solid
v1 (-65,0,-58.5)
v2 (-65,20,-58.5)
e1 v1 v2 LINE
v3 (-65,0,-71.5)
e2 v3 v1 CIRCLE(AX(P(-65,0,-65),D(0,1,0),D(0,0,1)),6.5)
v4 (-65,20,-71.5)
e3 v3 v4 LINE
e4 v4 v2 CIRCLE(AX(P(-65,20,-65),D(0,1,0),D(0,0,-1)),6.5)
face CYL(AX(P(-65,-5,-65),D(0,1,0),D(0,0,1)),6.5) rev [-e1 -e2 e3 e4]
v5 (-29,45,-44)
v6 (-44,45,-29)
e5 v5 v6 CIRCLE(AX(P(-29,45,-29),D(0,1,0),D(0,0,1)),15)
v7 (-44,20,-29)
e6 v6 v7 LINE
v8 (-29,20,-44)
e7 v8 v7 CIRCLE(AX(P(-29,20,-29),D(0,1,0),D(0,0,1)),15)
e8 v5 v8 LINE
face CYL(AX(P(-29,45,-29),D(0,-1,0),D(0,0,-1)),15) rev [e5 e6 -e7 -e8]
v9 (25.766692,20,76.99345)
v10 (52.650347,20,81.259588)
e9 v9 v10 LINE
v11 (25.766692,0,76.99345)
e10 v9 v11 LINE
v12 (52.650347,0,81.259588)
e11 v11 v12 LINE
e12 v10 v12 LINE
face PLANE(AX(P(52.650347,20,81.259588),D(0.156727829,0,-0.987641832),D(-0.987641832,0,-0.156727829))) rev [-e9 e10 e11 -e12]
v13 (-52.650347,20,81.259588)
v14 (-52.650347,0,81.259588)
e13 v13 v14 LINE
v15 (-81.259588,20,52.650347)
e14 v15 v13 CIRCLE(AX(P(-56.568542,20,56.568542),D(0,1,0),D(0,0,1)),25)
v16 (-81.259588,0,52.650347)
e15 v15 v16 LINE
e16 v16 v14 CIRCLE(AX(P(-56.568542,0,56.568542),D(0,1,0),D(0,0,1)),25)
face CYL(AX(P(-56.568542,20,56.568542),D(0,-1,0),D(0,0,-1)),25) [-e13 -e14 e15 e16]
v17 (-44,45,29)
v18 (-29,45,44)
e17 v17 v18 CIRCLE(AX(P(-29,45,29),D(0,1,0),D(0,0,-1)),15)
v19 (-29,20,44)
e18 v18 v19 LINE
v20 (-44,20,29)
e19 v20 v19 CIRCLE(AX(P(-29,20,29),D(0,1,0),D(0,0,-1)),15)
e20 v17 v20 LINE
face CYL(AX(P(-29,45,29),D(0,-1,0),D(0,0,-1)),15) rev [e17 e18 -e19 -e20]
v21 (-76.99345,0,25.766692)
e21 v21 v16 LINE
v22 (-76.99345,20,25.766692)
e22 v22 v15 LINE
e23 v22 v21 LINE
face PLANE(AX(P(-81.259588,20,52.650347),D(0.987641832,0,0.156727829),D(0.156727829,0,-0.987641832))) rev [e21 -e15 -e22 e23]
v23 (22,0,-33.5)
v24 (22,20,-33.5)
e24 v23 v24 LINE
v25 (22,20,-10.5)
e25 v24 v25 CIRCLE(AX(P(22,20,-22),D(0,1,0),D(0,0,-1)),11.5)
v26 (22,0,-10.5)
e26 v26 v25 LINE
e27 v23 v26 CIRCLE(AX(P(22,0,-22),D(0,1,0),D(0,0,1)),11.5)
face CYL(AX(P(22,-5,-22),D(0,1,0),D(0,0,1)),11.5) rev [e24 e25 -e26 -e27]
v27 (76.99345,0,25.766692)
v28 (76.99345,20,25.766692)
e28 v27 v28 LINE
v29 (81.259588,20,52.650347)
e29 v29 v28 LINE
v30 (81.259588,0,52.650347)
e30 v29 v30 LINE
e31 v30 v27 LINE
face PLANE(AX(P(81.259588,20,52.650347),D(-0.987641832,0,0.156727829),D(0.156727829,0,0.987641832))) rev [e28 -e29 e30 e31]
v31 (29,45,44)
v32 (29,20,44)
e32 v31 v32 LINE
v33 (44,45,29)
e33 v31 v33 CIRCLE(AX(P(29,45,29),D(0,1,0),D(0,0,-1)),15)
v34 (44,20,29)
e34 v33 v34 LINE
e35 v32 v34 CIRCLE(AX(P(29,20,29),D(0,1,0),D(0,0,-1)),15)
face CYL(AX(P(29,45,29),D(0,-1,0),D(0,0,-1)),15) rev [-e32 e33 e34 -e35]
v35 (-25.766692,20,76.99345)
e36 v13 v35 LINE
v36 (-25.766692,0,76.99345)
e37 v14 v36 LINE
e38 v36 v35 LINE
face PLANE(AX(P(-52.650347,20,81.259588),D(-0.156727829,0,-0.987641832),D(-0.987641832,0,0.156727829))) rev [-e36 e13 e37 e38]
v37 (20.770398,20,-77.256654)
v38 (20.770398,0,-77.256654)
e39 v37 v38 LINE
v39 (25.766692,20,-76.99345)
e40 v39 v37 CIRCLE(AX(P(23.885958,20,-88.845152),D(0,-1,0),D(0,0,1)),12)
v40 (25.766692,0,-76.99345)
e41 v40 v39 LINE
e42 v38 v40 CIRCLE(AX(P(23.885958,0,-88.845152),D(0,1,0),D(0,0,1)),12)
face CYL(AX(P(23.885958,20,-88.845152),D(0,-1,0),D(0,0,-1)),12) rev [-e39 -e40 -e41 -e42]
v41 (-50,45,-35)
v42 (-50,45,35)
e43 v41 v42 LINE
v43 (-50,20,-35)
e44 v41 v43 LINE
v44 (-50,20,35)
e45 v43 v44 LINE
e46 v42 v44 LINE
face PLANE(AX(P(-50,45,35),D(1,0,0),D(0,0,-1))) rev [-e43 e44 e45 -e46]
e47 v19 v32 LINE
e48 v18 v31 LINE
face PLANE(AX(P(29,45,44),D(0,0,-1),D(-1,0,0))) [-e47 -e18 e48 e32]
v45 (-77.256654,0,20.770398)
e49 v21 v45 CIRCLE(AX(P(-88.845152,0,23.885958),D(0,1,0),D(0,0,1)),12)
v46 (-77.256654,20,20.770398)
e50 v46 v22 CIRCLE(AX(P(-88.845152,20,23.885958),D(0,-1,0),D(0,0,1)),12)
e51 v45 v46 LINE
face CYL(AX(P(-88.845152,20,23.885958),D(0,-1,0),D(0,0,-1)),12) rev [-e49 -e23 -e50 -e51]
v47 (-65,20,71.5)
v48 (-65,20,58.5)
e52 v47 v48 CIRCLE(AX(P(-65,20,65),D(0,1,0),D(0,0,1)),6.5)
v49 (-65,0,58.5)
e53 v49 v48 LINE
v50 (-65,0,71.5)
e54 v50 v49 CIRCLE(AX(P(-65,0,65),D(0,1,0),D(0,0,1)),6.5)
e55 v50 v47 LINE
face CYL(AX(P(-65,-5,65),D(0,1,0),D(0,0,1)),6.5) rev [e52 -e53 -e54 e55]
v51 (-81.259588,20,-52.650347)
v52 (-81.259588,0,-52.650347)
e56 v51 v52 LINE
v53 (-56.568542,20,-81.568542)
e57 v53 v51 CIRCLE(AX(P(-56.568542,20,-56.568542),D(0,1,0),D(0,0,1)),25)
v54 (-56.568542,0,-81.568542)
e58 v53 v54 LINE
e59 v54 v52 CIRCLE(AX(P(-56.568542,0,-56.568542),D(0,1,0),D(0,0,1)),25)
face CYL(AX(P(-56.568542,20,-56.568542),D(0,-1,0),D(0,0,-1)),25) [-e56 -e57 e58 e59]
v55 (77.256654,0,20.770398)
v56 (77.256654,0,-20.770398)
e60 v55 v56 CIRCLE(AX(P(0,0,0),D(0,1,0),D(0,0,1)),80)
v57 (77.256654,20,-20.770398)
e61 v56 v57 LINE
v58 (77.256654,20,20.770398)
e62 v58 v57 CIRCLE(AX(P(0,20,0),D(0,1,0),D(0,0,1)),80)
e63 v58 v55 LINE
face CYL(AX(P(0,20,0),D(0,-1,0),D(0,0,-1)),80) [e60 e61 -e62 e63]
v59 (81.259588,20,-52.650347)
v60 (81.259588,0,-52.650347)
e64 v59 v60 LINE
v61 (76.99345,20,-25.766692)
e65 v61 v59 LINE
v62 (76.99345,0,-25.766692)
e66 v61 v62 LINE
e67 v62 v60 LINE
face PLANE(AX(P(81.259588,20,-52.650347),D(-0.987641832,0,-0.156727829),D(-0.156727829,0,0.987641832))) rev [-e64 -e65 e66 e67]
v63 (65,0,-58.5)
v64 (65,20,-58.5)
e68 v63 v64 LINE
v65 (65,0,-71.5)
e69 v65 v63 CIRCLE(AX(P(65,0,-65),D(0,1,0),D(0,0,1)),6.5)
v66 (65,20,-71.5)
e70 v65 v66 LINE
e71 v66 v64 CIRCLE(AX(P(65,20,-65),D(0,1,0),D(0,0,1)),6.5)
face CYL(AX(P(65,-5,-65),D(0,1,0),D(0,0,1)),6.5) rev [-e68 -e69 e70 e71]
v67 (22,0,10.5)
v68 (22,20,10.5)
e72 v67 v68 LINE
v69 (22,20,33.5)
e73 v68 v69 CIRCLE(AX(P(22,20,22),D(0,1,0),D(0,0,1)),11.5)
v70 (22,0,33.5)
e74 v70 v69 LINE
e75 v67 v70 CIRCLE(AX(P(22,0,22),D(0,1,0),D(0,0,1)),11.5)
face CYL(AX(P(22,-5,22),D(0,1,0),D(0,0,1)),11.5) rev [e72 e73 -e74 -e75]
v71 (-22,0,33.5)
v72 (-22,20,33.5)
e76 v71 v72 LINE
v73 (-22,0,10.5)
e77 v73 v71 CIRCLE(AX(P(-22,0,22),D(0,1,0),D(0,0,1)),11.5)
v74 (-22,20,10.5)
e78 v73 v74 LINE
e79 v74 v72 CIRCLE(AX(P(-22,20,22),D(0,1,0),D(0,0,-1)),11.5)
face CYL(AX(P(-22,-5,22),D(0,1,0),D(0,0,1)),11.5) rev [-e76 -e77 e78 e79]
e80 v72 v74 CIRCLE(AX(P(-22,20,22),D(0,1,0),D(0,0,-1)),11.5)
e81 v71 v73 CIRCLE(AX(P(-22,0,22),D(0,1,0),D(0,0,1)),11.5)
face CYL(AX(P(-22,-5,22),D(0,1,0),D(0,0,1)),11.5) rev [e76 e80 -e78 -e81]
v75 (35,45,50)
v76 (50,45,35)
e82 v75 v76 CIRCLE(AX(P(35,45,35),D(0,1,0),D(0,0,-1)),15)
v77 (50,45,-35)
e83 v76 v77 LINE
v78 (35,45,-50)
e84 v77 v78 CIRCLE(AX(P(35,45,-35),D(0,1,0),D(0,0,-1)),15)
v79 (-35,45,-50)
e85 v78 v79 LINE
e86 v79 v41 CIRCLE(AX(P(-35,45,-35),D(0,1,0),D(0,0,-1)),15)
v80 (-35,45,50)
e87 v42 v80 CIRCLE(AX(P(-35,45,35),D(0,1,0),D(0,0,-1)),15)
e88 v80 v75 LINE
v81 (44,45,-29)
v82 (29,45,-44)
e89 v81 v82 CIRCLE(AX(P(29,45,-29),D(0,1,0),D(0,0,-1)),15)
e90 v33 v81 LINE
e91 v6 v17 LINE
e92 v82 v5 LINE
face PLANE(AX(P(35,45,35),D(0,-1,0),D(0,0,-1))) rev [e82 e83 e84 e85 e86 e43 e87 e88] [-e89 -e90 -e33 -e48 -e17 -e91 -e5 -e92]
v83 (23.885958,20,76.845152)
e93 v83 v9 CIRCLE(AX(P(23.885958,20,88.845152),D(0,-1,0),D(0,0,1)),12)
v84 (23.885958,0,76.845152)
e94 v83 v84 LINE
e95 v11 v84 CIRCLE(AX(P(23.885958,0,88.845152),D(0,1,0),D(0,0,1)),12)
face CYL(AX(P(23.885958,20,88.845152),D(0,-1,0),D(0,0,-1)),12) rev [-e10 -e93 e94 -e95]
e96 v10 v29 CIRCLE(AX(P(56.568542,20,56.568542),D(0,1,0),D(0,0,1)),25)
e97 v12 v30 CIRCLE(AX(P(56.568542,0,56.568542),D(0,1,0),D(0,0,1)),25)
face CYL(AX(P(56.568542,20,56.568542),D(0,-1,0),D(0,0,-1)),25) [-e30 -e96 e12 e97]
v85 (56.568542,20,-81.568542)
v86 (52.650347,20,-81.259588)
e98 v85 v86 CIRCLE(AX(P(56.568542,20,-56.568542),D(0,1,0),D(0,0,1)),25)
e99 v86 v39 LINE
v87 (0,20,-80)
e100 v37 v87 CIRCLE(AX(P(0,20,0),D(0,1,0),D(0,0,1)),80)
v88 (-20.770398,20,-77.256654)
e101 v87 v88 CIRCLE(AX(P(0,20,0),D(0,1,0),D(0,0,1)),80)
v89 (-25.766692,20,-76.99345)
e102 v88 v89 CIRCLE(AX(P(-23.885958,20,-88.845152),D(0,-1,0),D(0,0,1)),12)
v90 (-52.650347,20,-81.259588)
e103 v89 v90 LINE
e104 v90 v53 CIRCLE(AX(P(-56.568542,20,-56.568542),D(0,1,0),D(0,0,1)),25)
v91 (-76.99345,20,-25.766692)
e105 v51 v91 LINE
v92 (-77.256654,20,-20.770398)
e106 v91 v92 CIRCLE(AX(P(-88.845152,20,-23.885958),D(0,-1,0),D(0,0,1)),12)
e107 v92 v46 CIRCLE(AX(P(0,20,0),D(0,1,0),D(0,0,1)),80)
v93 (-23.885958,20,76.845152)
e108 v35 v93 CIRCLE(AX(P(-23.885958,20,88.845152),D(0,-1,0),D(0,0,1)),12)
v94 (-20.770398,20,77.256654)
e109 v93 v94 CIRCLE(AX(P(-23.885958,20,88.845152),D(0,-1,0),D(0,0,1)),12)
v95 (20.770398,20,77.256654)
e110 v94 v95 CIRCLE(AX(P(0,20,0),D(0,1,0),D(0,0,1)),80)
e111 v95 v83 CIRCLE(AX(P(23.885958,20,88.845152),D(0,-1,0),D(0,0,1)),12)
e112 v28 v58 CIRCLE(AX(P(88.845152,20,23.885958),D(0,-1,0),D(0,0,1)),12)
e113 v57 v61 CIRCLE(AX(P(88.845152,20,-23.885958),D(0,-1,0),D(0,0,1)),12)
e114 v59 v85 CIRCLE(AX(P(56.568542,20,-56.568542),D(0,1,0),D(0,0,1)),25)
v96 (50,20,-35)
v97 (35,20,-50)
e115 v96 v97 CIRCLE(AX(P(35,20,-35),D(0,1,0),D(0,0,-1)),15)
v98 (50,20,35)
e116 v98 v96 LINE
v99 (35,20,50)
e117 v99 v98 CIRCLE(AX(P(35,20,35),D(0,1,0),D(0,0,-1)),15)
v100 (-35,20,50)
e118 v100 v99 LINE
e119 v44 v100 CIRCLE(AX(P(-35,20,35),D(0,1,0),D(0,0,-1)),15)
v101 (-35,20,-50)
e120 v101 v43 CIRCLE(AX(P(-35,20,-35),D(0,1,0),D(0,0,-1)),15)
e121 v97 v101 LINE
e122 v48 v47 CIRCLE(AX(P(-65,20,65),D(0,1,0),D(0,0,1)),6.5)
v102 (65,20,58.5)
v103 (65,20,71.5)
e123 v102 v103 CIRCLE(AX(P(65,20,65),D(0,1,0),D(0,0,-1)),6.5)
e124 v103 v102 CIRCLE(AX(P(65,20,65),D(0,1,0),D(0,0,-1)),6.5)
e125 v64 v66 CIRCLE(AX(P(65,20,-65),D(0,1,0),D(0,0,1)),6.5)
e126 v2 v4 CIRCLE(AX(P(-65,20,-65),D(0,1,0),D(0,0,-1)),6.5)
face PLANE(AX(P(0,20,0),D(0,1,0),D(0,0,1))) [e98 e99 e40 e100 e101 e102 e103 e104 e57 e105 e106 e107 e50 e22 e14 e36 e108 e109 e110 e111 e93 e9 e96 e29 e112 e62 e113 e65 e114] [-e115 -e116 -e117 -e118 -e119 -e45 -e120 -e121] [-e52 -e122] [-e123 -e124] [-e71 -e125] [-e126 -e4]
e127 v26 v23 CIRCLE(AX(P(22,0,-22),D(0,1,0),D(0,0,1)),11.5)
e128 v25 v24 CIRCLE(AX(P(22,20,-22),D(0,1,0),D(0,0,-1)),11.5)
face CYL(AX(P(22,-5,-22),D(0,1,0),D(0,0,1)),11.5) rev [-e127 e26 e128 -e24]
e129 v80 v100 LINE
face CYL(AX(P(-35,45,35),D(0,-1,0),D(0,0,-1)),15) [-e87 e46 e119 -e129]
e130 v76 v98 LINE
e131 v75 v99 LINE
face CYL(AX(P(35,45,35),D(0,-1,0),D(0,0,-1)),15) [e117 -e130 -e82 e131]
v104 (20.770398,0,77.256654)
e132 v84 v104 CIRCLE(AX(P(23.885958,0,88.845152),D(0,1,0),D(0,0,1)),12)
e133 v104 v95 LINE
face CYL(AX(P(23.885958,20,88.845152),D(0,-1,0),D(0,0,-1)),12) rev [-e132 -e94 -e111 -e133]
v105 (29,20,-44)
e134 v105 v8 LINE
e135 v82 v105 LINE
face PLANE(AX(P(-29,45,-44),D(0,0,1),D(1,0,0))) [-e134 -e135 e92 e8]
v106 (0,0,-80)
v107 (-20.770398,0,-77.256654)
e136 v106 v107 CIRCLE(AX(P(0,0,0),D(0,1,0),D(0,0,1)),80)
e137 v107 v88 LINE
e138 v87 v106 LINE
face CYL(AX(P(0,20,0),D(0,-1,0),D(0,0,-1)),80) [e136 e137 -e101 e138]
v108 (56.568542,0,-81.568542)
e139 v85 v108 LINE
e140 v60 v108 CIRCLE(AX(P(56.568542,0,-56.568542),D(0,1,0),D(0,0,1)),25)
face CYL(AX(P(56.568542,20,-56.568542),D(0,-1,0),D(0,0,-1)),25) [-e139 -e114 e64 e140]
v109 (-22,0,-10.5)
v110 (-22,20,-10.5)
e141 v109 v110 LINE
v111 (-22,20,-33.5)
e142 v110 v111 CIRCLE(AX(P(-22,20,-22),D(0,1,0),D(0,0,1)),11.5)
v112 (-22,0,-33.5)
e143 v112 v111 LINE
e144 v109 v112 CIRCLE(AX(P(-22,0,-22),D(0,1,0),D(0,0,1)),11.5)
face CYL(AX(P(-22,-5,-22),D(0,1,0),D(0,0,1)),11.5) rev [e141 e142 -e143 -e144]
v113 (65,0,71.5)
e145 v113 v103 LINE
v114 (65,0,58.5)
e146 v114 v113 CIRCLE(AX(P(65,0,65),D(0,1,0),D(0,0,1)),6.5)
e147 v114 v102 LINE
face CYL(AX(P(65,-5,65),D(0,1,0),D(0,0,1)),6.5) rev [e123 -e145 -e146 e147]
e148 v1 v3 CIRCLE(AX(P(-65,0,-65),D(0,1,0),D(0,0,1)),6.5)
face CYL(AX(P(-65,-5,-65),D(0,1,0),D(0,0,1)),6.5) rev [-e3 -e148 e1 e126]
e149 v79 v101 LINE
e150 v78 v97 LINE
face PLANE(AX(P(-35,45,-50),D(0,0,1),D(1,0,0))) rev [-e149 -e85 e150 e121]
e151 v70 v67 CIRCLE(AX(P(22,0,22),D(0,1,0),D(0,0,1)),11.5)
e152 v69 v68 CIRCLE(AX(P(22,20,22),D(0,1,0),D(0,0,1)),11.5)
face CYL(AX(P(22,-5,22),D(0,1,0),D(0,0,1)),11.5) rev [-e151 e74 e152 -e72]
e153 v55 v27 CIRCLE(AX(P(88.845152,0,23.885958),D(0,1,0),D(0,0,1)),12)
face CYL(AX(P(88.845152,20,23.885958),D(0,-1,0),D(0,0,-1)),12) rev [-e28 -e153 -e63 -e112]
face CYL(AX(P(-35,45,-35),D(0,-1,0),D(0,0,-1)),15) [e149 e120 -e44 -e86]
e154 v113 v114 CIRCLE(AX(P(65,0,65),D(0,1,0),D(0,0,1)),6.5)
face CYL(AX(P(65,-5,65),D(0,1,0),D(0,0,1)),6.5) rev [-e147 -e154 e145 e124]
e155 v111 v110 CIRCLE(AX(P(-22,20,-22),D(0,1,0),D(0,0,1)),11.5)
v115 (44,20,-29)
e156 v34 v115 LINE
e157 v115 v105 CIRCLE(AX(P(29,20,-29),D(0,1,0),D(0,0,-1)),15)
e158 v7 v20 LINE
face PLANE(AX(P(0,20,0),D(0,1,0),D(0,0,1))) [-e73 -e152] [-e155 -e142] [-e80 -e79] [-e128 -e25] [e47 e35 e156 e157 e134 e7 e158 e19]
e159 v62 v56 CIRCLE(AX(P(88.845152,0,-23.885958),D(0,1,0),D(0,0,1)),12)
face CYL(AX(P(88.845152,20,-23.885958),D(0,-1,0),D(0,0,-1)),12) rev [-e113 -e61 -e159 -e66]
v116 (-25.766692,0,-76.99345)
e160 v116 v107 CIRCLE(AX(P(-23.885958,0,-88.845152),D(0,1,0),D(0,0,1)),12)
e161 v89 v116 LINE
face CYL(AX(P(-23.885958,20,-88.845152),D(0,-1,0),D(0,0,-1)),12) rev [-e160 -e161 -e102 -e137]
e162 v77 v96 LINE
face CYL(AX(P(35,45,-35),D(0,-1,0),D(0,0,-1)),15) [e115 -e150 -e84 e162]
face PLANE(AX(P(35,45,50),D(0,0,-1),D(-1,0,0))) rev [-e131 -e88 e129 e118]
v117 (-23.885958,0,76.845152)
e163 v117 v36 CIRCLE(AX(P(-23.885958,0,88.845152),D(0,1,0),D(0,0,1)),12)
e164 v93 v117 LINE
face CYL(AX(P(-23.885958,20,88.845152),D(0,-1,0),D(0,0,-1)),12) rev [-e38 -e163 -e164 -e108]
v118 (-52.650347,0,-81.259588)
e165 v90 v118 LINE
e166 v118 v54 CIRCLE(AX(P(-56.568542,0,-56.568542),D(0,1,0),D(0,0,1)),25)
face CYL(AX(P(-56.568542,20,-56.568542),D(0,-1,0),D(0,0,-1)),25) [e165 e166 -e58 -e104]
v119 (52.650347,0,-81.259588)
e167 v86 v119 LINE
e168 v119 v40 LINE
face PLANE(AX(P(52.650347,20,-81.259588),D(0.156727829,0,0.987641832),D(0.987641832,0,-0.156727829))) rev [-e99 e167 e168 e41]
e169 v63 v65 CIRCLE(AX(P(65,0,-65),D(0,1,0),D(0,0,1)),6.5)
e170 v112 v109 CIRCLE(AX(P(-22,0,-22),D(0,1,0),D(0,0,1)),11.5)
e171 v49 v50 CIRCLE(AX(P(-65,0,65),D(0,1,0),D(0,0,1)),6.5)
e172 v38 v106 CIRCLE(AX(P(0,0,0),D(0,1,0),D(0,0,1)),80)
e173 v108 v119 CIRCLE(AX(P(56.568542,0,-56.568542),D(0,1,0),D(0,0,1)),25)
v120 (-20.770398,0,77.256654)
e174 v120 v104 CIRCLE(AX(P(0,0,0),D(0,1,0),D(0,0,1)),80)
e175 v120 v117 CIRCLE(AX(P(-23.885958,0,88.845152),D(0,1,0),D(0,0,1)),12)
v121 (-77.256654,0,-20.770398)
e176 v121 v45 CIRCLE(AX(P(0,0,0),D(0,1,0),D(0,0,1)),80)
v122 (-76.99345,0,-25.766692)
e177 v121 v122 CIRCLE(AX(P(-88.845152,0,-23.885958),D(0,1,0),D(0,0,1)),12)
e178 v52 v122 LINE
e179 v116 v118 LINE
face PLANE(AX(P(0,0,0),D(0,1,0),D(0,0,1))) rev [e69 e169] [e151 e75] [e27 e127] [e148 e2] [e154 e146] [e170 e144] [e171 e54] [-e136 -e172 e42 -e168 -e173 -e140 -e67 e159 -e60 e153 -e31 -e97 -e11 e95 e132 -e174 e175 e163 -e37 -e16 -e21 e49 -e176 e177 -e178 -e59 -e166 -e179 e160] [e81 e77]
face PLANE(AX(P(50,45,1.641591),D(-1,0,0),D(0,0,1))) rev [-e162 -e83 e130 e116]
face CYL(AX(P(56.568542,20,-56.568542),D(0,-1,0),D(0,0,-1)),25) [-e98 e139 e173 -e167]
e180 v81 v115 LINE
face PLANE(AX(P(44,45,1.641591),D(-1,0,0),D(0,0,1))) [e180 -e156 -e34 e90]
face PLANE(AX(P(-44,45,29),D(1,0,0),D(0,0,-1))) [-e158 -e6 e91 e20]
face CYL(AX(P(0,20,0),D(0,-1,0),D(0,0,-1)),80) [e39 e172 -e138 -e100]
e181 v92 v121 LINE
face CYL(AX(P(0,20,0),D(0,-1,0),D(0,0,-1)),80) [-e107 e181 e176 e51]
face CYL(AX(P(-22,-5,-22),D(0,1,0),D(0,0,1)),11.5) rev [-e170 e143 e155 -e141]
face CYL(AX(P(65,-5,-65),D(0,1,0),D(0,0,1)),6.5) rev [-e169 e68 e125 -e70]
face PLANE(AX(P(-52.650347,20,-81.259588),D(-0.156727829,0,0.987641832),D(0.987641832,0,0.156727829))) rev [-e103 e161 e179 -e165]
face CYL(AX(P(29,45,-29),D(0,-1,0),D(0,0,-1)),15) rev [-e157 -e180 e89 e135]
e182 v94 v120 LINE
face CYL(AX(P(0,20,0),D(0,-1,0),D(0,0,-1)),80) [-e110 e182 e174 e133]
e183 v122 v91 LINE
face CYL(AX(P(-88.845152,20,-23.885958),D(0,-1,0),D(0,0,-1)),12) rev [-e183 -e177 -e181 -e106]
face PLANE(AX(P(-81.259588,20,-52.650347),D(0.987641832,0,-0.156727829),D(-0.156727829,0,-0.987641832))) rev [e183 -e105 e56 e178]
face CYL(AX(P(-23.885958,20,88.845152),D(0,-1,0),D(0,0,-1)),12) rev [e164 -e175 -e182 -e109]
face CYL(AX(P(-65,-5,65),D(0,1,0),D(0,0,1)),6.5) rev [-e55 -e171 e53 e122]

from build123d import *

# Parameters (mm, degrees)
LOBED_BASE_PLATE_DEPTH      = 20
SQUARE_POCKET_WALL_DEPTH    = 25
POCKET_HOLES_SKETCH_R       = 11.5
POCKET_FLOOR_HOLES_4X_DEPTH = 25
EDGE_FILLET_R12_A_R         = 12
EDGE_FILLET_R12_B_R         = 12
EDGE_FILLET_R12_C_R         = 12
EDGE_FILLET_R12_D_R         = 12
EDGE_FILLET_R12_E_R         = 12
EDGE_FILLET_R12_F_R         = 12
EDGE_FILLET_R12_G_R         = 12
EDGE_FILLET_R12_H_R         = 12
MOUNTING_HOLES_SKETCH_R     = 6.5
MOUNTING_HOLES_4X_DEPTH     = 25


with BuildPart() as part:
    # Lobed Base Profile → Lobed Base Plate (new body)
    with BuildSketch(Plane(origin=(0, 0, 0), x_dir=(1, 0, 0), z_dir=(0, 1, 0))):
        with BuildLine():
            Line((52.650346772, -81.259588286), (23.147950432, -76.577884476))
            ThreePointArc((23.147950432, -76.577884476), (0, -80), (-23.147950432, -76.577884476))
            Line((-23.147950432, -76.577884476), (-52.650346772, -81.259588286))
            ThreePointArc((-52.650346772, -81.259588286), (-74.246212025, -74.246212025), (-81.259588286, -52.650346772))
            Line((-81.259588286, -52.650346772), (-76.577884476, -23.147950432))
            ThreePointArc((-76.577884476, -23.147950432), (-80, 0), (-76.577884476, 23.147950432))
            Line((-76.577884476, 23.147950432), (-81.259588286, 52.650346772))
            ThreePointArc((-81.259588286, 52.650346772), (-74.246212025, 74.246212025), (-52.650346772, 81.259588286))
            Line((-52.650346772, 81.259588286), (-23.147950432, 76.577884476))
            ThreePointArc((-23.147950432, 76.577884476), (0, 80), (23.147950432, 76.577884476))
            Line((23.147950432, 76.577884476), (52.650346772, 81.259588286))
            ThreePointArc((52.650346772, 81.259588286), (74.246212025, 74.246212025), (81.259588286, 52.650346772))
            Line((81.259588286, 52.650346772), (76.577884476, 23.147950432))
            ThreePointArc((76.577884476, 23.147950432), (80, 0), (76.577884476, -23.147950432))
            Line((76.577884476, -23.147950432), (81.259588286, -52.650346772))
            ThreePointArc((81.259588286, -52.650346772), (74.246212025, -74.246212025), (52.650346772, -81.259588286))
        make_face()
    extrude(amount=LOBED_BASE_PLATE_DEPTH)

    # Square Wall Profile → Square Pocket Wall (add)
    with BuildSketch(Plane(origin=(0, 20, 0), x_dir=(1, 0, 0), z_dir=(0, 1, 0))):
        with BuildLine():
            Line((50, -1.641590962), (50, -35))
            ThreePointArc((50, -35), (45.606601718, -45.606601718), (35, -50))
            Line((35, -50), (-35, -50))
            ThreePointArc((-35, -50), (-45.606601718, -45.606601718), (-50, -35))
            Line((-50, -35), (-50, 35))
            ThreePointArc((-50, 35), (-45.606601718, 45.606601718), (-35, 50))
            Line((-35, 50), (35, 50))
            ThreePointArc((35, 50), (45.606601718, 45.606601718), (50, 35))
            Line((50, 35), (50, -1.641590962))
        make_face()
        with BuildLine():
            Line((44, -1.641590962), (44, -29))
            ThreePointArc((44, -29), (39.606601718, -39.606601718), (29, -44))
            Line((29, -44), (-29, -44))
            ThreePointArc((-29, -44), (-39.606601718, -39.606601718), (-44, -29))
            Line((-44, -29), (-44, 29))
            ThreePointArc((-44, 29), (-39.606601718, 39.606601718), (-29, 44))
            Line((-29, 44), (29, 44))
            ThreePointArc((29, 44), (39.606601718, 39.606601718), (44, 29))
            Line((44, 29), (44, -1.641590962))
        make_face(mode=Mode.SUBTRACT)
    extrude(amount=SQUARE_POCKET_WALL_DEPTH)

    # Pocket Holes Sketch → Pocket Floor Holes 4x (cut)
    with BuildSketch(Plane(origin=(0, 20, 0), x_dir=(1, 0, 0), z_dir=(0, 1, 0))):
        with Locations(Location((22, -22, 0), (0, 0, 270))):
            Circle(POCKET_HOLES_SKETCH_R)
        with Locations(Location((22, 22, 0), (0, 0, 270))):
            Circle(POCKET_HOLES_SKETCH_R)
        with Locations(Location((-22, 22, 0), (0, 0, 270))):
            Circle(POCKET_HOLES_SKETCH_R)
        with Locations(Location((-22, -22, 0), (0, 0, 270))):
            Circle(POCKET_HOLES_SKETCH_R)
    extrude(amount=-POCKET_FLOOR_HOLES_4X_DEPTH, mode=Mode.SUBTRACT)

    # Edge Fillet R12 A
    edge_fillet_r12_a_edges = [part.edges().sort_by_distance(p)[0] for p in [
        (23.147950432, 10, 76.577884476),
    ]]
    fillet(edge_fillet_r12_a_edges, radius=EDGE_FILLET_R12_A_R)

    # Edge Fillet R12 B
    edge_fillet_r12_b_edges = [part.edges().sort_by_distance(p)[0] for p in [
        (-23.147950432, 10, 76.577884476),
    ]]
    fillet(edge_fillet_r12_b_edges, radius=EDGE_FILLET_R12_B_R)

    # Edge Fillet R12 C
    edge_fillet_r12_c_edges = [part.edges().sort_by_distance(p)[0] for p in [
        (23.147950432, 10, -76.577884476),
    ]]
    fillet(edge_fillet_r12_c_edges, radius=EDGE_FILLET_R12_C_R)

    # Edge Fillet R12 D
    edge_fillet_r12_d_edges = [part.edges().sort_by_distance(p)[0] for p in [
        (-23.147950432, 10, -76.577884476),
    ]]
    fillet(edge_fillet_r12_d_edges, radius=EDGE_FILLET_R12_D_R)

    # Edge Fillet R12 E
    edge_fillet_r12_e_edges = [part.edges().sort_by_distance(p)[0] for p in [
        (76.577884476, 10, -23.147950432),
    ]]
    fillet(edge_fillet_r12_e_edges, radius=EDGE_FILLET_R12_E_R)

    # Edge Fillet R12 F
    edge_fillet_r12_f_edges = [part.edges().sort_by_distance(p)[0] for p in [
        (76.577884476, 10, 23.147950432),
    ]]
    fillet(edge_fillet_r12_f_edges, radius=EDGE_FILLET_R12_F_R)

    # Edge Fillet R12 G
    edge_fillet_r12_g_edges = [part.edges().sort_by_distance(p)[0] for p in [
        (-76.577884476, 10, 23.147950432),
    ]]
    fillet(edge_fillet_r12_g_edges, radius=EDGE_FILLET_R12_G_R)

    # Edge Fillet R12 H
    edge_fillet_r12_h_edges = [part.edges().sort_by_distance(p)[0] for p in [
        (-76.577884476, 10, -23.147950432),
    ]]
    fillet(edge_fillet_r12_h_edges, radius=EDGE_FILLET_R12_H_R)

    # Mounting Holes Sketch → Mounting Holes 4x (cut)
    with BuildSketch(Plane(origin=(0, 20, 0), x_dir=(1, 0, 0), z_dir=(0, 1, 0))):
        with Locations(Location((65, 65, 0), (0, 0, 270))):
            Circle(MOUNTING_HOLES_SKETCH_R)
        with Locations(Location((65, -65, 0), (0, 0, 270))):
            Circle(MOUNTING_HOLES_SKETCH_R)
        with Locations(Location((-65, -65, 0), (0, 0, 270))):
            Circle(MOUNTING_HOLES_SKETCH_R)
        with Locations(Location((-65, 65, 0), (0, 0, 270))):
            Circle(MOUNTING_HOLES_SKETCH_R)
    extrude(amount=-MOUNTING_HOLES_4X_DEPTH, mode=Mode.SUBTRACT)


solid = part.part
